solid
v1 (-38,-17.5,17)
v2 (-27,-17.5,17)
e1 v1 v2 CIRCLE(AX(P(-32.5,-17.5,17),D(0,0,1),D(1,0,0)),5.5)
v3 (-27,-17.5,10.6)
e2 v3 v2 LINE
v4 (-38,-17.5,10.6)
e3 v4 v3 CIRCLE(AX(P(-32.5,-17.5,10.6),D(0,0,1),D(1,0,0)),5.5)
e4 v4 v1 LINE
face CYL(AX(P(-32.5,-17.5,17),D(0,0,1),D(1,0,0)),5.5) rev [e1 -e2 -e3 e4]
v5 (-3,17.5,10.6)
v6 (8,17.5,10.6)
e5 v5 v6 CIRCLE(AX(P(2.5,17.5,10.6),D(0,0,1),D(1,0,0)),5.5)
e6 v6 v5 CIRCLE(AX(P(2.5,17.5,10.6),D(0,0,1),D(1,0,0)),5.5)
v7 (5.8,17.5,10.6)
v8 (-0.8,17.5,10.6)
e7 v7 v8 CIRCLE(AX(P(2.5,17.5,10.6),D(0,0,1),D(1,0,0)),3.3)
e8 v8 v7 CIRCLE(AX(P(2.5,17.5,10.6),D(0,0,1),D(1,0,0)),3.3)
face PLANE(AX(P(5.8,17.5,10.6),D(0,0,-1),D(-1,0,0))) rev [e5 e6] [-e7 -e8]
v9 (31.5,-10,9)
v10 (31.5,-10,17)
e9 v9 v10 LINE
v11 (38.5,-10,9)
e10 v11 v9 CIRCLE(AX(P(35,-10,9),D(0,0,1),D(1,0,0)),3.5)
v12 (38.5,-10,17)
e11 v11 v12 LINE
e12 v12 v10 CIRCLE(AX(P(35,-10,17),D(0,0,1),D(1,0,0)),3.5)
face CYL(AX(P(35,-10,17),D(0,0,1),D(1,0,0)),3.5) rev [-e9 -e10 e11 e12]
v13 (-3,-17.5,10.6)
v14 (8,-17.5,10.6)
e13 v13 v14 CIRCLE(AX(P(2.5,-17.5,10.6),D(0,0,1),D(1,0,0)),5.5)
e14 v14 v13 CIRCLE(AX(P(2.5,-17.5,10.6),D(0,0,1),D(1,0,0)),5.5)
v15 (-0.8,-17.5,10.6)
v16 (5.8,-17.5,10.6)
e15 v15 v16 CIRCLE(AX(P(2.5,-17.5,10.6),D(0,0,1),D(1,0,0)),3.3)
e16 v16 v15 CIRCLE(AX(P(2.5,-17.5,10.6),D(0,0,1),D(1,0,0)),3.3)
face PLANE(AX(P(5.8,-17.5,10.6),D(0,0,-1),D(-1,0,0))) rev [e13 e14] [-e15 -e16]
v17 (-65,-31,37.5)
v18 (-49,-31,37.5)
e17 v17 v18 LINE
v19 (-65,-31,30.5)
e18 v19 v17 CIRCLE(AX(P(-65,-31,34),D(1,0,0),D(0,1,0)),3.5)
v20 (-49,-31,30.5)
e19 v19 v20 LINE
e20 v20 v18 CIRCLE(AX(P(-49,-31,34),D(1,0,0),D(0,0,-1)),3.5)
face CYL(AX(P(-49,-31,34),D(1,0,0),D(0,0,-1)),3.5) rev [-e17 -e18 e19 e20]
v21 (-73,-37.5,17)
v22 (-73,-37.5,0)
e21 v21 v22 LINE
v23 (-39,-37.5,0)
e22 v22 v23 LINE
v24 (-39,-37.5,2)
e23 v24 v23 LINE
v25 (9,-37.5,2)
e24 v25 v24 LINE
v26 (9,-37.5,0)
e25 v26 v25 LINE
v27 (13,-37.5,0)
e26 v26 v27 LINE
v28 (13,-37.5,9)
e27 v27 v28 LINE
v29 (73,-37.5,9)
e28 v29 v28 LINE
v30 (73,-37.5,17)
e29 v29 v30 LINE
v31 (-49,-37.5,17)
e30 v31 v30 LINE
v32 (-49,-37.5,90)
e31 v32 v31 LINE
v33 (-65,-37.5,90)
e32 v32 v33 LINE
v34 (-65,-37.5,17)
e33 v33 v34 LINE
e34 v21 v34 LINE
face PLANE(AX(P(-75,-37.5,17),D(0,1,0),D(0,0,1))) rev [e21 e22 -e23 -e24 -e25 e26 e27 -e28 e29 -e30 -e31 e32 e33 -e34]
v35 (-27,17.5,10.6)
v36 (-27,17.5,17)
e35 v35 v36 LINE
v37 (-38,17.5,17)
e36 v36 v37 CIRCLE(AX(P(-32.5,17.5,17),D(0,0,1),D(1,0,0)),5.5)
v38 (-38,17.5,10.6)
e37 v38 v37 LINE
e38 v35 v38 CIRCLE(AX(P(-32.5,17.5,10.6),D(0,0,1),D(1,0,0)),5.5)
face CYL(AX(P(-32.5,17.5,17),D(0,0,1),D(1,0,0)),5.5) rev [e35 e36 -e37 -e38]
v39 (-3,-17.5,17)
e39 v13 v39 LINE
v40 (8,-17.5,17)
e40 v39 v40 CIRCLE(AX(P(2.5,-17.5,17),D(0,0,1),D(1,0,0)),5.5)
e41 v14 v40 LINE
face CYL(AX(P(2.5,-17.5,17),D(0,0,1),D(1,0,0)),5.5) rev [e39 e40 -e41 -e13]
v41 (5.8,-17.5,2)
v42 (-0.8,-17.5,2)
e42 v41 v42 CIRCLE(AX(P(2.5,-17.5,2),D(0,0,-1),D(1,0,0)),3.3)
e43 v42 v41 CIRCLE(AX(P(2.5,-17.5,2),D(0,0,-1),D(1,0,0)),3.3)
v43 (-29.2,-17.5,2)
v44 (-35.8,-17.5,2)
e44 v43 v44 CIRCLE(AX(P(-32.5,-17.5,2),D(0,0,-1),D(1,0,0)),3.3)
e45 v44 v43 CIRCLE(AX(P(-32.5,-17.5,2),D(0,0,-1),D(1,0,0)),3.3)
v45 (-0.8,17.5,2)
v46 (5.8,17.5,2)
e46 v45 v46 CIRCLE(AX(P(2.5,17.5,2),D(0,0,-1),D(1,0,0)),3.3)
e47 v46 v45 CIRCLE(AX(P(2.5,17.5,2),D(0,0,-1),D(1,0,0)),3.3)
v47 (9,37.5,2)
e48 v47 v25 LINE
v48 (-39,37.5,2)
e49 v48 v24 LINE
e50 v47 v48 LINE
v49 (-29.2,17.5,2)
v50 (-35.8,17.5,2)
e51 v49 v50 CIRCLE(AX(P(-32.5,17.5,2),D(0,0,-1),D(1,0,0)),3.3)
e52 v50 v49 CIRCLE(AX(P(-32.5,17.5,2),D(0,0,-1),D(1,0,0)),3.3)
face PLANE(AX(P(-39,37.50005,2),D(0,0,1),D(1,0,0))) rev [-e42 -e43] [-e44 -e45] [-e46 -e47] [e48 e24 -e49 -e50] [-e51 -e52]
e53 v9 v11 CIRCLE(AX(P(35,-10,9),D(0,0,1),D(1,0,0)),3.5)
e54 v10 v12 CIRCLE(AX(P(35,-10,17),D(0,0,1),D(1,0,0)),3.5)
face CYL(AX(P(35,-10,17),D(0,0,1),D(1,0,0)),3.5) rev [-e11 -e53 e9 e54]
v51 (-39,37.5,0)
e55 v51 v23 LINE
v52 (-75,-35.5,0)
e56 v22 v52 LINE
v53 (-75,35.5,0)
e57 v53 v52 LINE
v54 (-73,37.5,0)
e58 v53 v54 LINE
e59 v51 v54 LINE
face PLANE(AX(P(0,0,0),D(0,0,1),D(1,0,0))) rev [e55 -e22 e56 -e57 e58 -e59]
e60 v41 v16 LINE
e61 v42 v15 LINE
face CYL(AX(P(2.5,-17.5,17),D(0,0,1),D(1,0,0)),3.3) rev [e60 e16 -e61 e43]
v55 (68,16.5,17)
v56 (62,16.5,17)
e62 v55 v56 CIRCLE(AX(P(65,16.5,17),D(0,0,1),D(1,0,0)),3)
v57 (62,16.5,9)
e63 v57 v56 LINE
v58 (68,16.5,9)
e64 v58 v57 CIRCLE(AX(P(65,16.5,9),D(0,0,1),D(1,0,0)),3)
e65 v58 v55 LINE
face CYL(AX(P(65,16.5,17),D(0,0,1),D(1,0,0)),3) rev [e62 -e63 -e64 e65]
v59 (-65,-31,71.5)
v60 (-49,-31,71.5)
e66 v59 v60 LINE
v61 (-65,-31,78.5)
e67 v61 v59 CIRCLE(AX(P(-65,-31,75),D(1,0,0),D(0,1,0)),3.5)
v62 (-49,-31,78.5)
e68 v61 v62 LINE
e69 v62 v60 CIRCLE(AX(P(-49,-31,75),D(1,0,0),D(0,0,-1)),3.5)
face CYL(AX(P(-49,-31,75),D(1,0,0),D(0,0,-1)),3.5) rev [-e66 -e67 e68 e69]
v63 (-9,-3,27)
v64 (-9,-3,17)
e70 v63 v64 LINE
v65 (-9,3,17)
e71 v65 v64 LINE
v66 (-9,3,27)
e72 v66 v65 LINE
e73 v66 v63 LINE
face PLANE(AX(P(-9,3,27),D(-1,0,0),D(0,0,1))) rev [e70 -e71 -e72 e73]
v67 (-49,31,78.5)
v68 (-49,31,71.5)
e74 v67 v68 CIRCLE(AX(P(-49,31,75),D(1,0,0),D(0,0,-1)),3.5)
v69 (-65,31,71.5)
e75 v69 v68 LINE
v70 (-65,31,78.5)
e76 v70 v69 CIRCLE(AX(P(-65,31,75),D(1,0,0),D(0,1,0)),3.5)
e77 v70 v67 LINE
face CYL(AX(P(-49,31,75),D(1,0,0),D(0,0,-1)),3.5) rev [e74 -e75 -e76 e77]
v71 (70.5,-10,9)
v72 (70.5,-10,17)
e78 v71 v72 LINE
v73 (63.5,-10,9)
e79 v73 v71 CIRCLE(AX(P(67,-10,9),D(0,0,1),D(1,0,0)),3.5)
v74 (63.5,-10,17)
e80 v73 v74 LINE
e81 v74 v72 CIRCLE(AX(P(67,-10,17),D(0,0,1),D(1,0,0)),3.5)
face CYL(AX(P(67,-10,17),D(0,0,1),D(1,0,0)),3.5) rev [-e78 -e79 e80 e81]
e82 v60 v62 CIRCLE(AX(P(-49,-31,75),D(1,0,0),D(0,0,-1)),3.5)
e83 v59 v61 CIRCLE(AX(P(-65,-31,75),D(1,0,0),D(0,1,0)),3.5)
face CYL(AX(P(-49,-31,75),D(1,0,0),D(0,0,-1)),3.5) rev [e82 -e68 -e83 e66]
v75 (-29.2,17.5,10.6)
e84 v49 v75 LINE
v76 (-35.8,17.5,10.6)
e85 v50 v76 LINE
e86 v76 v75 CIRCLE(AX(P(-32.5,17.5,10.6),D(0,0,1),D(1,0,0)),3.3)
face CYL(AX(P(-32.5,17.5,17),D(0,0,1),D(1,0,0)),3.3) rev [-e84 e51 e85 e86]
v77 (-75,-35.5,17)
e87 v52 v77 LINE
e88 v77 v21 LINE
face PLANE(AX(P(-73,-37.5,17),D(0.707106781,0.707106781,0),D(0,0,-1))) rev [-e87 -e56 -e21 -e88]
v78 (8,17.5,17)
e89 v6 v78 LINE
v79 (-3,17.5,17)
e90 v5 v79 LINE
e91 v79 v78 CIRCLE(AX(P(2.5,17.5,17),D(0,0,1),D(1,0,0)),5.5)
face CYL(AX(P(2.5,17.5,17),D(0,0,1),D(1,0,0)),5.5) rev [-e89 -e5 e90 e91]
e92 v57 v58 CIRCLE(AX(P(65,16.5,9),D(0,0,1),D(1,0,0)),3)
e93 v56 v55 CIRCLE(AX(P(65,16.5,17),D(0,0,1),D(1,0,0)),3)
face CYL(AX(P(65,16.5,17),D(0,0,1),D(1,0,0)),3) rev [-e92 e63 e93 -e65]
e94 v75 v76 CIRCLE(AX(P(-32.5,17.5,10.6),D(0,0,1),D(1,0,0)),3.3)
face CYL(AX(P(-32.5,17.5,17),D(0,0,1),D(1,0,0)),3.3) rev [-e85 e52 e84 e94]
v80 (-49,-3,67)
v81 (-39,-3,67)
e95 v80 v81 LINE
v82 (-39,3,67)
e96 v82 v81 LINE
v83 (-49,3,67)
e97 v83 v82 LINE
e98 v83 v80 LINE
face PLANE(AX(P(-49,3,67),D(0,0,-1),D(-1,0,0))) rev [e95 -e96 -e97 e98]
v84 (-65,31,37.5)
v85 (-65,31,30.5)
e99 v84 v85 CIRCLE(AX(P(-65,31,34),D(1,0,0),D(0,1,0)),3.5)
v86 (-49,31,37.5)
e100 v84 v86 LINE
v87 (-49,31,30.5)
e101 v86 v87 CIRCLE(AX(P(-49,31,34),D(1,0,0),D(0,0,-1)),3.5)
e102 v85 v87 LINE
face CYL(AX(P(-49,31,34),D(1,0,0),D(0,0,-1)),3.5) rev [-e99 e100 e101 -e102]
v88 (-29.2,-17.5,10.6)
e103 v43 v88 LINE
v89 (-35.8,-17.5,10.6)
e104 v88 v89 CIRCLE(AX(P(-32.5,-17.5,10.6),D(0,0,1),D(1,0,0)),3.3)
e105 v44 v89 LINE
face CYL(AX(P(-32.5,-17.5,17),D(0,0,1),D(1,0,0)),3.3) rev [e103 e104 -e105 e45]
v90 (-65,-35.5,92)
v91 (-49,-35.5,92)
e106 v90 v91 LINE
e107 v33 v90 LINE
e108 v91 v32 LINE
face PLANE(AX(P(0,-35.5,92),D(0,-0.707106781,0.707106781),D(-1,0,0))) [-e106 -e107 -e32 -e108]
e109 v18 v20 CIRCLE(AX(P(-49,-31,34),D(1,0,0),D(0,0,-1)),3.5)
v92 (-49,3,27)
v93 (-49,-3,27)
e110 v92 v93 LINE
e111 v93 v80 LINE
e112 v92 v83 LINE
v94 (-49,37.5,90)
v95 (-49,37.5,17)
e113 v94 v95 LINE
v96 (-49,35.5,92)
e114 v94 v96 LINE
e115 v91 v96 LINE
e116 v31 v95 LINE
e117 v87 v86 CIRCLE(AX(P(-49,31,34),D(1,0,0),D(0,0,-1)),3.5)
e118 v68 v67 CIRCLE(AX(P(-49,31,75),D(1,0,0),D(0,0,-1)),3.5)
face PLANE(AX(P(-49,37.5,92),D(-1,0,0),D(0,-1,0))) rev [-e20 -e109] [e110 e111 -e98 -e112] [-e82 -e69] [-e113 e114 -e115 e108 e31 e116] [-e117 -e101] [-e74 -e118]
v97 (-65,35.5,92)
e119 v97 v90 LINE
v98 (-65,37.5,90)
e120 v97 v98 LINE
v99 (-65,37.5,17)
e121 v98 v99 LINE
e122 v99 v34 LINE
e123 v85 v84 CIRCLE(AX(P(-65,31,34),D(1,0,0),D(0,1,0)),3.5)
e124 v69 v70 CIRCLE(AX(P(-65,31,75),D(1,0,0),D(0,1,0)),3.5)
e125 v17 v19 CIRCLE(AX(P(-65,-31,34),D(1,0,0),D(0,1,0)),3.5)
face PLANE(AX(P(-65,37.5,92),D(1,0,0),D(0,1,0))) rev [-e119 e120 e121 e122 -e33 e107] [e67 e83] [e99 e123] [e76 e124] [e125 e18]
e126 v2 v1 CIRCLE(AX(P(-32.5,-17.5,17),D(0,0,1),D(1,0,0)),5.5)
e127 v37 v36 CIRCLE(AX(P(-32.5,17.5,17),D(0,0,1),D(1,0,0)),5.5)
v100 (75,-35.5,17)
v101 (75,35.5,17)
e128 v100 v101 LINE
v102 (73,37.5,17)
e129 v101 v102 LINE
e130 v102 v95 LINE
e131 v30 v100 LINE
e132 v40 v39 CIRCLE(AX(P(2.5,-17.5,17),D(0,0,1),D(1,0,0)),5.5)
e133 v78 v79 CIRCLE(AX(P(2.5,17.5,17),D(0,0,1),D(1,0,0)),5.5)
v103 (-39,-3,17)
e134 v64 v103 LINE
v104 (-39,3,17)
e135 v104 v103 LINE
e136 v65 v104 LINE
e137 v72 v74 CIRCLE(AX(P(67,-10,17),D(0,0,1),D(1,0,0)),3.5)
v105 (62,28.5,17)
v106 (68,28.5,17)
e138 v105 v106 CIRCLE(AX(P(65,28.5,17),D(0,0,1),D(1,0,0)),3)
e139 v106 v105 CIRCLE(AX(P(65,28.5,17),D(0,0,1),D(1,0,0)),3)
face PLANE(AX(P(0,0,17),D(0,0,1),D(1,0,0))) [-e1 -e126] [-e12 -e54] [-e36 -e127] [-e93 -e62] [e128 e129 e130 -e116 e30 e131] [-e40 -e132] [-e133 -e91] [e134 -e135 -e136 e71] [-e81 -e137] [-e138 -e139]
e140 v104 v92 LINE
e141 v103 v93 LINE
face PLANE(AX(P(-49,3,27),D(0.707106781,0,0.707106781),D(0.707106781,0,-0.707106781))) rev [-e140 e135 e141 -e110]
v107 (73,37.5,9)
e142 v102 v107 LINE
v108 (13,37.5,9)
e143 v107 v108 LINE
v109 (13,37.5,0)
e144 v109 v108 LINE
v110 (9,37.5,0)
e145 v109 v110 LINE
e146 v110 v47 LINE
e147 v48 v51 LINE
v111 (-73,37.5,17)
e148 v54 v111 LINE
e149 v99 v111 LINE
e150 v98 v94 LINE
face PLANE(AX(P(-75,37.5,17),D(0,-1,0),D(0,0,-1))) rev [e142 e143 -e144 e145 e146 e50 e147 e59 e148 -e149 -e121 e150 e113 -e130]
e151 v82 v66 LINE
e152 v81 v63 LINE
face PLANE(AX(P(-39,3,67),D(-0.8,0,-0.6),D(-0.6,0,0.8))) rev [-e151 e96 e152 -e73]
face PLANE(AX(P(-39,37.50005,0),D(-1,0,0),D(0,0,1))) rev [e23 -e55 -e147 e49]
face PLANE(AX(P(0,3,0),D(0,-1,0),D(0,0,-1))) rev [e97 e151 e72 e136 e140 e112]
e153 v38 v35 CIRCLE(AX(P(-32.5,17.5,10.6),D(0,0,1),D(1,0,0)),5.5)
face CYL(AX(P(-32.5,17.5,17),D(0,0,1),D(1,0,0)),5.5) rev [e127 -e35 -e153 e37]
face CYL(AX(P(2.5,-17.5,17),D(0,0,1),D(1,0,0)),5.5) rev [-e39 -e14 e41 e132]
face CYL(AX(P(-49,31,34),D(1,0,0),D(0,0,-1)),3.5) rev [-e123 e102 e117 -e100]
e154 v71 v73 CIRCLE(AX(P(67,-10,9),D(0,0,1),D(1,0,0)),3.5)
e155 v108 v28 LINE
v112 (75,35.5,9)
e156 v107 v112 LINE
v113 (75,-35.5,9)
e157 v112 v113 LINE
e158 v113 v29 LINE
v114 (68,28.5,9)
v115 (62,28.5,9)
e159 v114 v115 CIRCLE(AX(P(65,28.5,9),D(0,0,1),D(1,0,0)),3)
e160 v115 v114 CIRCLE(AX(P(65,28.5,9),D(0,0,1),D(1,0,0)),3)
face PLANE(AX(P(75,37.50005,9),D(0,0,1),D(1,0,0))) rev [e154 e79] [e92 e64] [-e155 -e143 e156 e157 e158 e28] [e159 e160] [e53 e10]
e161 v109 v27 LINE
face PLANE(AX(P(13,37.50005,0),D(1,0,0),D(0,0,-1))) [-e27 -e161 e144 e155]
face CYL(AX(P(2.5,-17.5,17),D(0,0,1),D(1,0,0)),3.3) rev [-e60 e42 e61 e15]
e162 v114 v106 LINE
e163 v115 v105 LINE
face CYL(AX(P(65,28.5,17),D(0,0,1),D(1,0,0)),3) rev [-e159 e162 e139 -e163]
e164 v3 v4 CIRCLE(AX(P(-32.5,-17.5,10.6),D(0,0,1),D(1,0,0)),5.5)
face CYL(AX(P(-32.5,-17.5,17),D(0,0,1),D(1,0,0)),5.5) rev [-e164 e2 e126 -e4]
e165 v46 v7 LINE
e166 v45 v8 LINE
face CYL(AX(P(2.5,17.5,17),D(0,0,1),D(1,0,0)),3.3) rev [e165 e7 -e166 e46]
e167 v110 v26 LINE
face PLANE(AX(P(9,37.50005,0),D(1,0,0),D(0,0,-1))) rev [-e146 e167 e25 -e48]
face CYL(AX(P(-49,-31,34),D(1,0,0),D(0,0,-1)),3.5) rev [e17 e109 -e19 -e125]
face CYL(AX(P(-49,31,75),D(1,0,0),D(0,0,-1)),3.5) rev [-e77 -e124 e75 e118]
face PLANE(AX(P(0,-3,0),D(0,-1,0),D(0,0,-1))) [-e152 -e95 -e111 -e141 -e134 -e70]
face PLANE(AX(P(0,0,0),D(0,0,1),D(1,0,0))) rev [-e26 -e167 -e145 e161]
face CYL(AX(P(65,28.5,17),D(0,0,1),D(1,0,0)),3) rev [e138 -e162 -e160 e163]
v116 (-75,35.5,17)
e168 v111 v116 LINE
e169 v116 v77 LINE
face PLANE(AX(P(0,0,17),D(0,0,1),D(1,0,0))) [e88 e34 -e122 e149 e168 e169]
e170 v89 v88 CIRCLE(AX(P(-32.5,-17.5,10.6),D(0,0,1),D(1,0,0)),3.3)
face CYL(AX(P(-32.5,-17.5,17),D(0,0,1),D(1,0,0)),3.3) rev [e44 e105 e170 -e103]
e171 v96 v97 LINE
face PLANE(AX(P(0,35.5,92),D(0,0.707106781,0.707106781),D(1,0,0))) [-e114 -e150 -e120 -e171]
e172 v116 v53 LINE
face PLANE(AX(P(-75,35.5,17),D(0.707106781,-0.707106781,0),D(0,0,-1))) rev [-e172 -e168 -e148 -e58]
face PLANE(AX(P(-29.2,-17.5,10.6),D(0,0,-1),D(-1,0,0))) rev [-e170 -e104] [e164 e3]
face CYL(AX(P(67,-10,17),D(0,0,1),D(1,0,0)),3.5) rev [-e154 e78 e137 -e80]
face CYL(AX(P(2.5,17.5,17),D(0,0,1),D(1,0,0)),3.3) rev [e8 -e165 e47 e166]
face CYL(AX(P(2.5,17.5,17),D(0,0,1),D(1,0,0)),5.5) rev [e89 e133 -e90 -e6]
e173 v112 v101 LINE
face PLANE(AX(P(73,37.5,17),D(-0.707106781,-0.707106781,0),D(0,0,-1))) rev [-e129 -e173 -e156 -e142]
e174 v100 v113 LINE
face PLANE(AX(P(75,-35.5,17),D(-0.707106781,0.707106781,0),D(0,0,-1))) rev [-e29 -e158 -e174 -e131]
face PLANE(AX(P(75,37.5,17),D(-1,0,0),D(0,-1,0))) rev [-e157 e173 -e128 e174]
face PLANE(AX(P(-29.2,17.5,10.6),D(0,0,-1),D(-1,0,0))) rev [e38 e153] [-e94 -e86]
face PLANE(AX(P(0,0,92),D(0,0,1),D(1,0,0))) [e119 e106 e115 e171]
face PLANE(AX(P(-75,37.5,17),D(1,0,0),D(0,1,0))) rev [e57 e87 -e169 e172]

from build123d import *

# Parameters (mm, degrees)
SKETCH_1_W                   = 150
SKETCH_1_H                   = 75
EXTRUDE_1_DEPTH              = 17
HOLE_WIZARD_M6_1_D           = 6.6
HOLE_WIZARD_M6_1_CBORE_D     = 11
HOLE_WIZARD_M6_1_CBORE_DEPTH = 6.4
SKETCH_8_W                   = 16
SKETCH_8_H                   = 75
EXTRUDE_2_DEPTH              = 75
HOLE_WIZARD_7_0_7_1_D        = 7
SKETCH_11_W                  = 48
SKETCH_11_H                  = 2
CUT_EXTRUDE_1_DEPTH          = 141.406552554
EXTRUDE_3_DEPTH              = 3
CHAMFER_1_SIZE               = 2
SKETCH_13_W                  = 62
SKETCH_13_H                  = 9
CUT_EXTRUDE_2_DEPTH          = 141.406552554
HOLE_WIZARD_7_0_7_2_D        = 7
HOLE_WIZARD_6_0_6_1_D        = 6


with BuildPart() as part:
    # 草图1 → 凸台-拉伸1 (new body)
    with BuildSketch(Plane.XY):
        Rectangle(SKETCH_1_W, SKETCH_1_H)
    extrude(amount=EXTRUDE_1_DEPTH)

    # M6 六角凹头螺钉的柱形沉头孔1 (through all)
    with Locations(Plane.XY.offset(17)):
        with Locations((2.5, 17.5), (-32.5, 17.5), (-32.5, -17.5), (2.5, -17.5)):
            CounterBoreHole(HOLE_WIZARD_M6_1_D / 2, HOLE_WIZARD_M6_1_CBORE_D / 2, HOLE_WIZARD_M6_1_CBORE_DEPTH)

    # 草图8 → 凸台-拉伸2 (add)
    with BuildSketch(Plane.XY.offset(17)):
        with Locations((-57, 0)):
            Rectangle(SKETCH_8_W, SKETCH_8_H)
    extrude(amount=EXTRUDE_2_DEPTH)

    # Ø7.0 (7) 直径孔1 (through all)
    with Locations(Plane(origin=(-49, 0, 0), x_dir=(0, 0, -1), z_dir=(1, 0, 0))):
        with Locations((-75, 31), (-75, -31), (-34, -31), (-34, 31)):
            Hole(HOLE_WIZARD_7_0_7_1_D / 2)

    # 草图11 → 切除-拉伸1 (cut, through all)
    with BuildSketch(Plane.XZ.offset(37.5)):
        with Locations((-15, 1)):
            Rectangle(SKETCH_11_W, SKETCH_11_H)
    extrude(amount=-CUT_EXTRUDE_1_DEPTH, mode=Mode.SUBTRACT)

    # 草图12 → 凸台-拉伸3 (add, symmetric)
    with BuildSketch(Plane(origin=(0, 0, 0), x_dir=(1, 0, 0), z_dir=(0, 1, 0))):
        Polygon((-49, -67), (-39, -67), (-9, -27), (-9, -17), (-39, -17), (-49, -27), align=None)
    extrude(amount=EXTRUDE_3_DEPTH, both=True)

    # 倒角1
    chamfer_1_edges = [part.edges().sort_by_distance(p)[0] for p in [
        (75, -37.5, 8.5),
        (75, 37.5, 8.5),
        (-57, -37.5, 92),
        (-57, 37.5, 92),
        (-75, 37.5, 8.5),
        (-75, -37.5, 8.5),
    ]]
    chamfer(chamfer_1_edges, length=CHAMFER_1_SIZE)

    # 草图13 → 切除-拉伸2 (cut, through all)
    with BuildSketch(Plane.XZ.offset(37.5)):
        with Locations((44, 4.5)):
            Rectangle(SKETCH_13_W, SKETCH_13_H)
    extrude(amount=-CUT_EXTRUDE_2_DEPTH, mode=Mode.SUBTRACT)

    # Ø7.0 (7) 直径孔2 (through all)
    with Locations(Plane.XY.offset(17)):
        with Locations((35, -10), (67, -10)):
            Hole(HOLE_WIZARD_7_0_7_2_D / 2)

    # Ø6.0 (6) 直径孔1 (through all)
    with Locations(Plane.XY.offset(17)):
        with Locations((65, 28.5), (65, 16.5)):
            Hole(HOLE_WIZARD_6_0_6_1_D / 2)


solid = part.part
